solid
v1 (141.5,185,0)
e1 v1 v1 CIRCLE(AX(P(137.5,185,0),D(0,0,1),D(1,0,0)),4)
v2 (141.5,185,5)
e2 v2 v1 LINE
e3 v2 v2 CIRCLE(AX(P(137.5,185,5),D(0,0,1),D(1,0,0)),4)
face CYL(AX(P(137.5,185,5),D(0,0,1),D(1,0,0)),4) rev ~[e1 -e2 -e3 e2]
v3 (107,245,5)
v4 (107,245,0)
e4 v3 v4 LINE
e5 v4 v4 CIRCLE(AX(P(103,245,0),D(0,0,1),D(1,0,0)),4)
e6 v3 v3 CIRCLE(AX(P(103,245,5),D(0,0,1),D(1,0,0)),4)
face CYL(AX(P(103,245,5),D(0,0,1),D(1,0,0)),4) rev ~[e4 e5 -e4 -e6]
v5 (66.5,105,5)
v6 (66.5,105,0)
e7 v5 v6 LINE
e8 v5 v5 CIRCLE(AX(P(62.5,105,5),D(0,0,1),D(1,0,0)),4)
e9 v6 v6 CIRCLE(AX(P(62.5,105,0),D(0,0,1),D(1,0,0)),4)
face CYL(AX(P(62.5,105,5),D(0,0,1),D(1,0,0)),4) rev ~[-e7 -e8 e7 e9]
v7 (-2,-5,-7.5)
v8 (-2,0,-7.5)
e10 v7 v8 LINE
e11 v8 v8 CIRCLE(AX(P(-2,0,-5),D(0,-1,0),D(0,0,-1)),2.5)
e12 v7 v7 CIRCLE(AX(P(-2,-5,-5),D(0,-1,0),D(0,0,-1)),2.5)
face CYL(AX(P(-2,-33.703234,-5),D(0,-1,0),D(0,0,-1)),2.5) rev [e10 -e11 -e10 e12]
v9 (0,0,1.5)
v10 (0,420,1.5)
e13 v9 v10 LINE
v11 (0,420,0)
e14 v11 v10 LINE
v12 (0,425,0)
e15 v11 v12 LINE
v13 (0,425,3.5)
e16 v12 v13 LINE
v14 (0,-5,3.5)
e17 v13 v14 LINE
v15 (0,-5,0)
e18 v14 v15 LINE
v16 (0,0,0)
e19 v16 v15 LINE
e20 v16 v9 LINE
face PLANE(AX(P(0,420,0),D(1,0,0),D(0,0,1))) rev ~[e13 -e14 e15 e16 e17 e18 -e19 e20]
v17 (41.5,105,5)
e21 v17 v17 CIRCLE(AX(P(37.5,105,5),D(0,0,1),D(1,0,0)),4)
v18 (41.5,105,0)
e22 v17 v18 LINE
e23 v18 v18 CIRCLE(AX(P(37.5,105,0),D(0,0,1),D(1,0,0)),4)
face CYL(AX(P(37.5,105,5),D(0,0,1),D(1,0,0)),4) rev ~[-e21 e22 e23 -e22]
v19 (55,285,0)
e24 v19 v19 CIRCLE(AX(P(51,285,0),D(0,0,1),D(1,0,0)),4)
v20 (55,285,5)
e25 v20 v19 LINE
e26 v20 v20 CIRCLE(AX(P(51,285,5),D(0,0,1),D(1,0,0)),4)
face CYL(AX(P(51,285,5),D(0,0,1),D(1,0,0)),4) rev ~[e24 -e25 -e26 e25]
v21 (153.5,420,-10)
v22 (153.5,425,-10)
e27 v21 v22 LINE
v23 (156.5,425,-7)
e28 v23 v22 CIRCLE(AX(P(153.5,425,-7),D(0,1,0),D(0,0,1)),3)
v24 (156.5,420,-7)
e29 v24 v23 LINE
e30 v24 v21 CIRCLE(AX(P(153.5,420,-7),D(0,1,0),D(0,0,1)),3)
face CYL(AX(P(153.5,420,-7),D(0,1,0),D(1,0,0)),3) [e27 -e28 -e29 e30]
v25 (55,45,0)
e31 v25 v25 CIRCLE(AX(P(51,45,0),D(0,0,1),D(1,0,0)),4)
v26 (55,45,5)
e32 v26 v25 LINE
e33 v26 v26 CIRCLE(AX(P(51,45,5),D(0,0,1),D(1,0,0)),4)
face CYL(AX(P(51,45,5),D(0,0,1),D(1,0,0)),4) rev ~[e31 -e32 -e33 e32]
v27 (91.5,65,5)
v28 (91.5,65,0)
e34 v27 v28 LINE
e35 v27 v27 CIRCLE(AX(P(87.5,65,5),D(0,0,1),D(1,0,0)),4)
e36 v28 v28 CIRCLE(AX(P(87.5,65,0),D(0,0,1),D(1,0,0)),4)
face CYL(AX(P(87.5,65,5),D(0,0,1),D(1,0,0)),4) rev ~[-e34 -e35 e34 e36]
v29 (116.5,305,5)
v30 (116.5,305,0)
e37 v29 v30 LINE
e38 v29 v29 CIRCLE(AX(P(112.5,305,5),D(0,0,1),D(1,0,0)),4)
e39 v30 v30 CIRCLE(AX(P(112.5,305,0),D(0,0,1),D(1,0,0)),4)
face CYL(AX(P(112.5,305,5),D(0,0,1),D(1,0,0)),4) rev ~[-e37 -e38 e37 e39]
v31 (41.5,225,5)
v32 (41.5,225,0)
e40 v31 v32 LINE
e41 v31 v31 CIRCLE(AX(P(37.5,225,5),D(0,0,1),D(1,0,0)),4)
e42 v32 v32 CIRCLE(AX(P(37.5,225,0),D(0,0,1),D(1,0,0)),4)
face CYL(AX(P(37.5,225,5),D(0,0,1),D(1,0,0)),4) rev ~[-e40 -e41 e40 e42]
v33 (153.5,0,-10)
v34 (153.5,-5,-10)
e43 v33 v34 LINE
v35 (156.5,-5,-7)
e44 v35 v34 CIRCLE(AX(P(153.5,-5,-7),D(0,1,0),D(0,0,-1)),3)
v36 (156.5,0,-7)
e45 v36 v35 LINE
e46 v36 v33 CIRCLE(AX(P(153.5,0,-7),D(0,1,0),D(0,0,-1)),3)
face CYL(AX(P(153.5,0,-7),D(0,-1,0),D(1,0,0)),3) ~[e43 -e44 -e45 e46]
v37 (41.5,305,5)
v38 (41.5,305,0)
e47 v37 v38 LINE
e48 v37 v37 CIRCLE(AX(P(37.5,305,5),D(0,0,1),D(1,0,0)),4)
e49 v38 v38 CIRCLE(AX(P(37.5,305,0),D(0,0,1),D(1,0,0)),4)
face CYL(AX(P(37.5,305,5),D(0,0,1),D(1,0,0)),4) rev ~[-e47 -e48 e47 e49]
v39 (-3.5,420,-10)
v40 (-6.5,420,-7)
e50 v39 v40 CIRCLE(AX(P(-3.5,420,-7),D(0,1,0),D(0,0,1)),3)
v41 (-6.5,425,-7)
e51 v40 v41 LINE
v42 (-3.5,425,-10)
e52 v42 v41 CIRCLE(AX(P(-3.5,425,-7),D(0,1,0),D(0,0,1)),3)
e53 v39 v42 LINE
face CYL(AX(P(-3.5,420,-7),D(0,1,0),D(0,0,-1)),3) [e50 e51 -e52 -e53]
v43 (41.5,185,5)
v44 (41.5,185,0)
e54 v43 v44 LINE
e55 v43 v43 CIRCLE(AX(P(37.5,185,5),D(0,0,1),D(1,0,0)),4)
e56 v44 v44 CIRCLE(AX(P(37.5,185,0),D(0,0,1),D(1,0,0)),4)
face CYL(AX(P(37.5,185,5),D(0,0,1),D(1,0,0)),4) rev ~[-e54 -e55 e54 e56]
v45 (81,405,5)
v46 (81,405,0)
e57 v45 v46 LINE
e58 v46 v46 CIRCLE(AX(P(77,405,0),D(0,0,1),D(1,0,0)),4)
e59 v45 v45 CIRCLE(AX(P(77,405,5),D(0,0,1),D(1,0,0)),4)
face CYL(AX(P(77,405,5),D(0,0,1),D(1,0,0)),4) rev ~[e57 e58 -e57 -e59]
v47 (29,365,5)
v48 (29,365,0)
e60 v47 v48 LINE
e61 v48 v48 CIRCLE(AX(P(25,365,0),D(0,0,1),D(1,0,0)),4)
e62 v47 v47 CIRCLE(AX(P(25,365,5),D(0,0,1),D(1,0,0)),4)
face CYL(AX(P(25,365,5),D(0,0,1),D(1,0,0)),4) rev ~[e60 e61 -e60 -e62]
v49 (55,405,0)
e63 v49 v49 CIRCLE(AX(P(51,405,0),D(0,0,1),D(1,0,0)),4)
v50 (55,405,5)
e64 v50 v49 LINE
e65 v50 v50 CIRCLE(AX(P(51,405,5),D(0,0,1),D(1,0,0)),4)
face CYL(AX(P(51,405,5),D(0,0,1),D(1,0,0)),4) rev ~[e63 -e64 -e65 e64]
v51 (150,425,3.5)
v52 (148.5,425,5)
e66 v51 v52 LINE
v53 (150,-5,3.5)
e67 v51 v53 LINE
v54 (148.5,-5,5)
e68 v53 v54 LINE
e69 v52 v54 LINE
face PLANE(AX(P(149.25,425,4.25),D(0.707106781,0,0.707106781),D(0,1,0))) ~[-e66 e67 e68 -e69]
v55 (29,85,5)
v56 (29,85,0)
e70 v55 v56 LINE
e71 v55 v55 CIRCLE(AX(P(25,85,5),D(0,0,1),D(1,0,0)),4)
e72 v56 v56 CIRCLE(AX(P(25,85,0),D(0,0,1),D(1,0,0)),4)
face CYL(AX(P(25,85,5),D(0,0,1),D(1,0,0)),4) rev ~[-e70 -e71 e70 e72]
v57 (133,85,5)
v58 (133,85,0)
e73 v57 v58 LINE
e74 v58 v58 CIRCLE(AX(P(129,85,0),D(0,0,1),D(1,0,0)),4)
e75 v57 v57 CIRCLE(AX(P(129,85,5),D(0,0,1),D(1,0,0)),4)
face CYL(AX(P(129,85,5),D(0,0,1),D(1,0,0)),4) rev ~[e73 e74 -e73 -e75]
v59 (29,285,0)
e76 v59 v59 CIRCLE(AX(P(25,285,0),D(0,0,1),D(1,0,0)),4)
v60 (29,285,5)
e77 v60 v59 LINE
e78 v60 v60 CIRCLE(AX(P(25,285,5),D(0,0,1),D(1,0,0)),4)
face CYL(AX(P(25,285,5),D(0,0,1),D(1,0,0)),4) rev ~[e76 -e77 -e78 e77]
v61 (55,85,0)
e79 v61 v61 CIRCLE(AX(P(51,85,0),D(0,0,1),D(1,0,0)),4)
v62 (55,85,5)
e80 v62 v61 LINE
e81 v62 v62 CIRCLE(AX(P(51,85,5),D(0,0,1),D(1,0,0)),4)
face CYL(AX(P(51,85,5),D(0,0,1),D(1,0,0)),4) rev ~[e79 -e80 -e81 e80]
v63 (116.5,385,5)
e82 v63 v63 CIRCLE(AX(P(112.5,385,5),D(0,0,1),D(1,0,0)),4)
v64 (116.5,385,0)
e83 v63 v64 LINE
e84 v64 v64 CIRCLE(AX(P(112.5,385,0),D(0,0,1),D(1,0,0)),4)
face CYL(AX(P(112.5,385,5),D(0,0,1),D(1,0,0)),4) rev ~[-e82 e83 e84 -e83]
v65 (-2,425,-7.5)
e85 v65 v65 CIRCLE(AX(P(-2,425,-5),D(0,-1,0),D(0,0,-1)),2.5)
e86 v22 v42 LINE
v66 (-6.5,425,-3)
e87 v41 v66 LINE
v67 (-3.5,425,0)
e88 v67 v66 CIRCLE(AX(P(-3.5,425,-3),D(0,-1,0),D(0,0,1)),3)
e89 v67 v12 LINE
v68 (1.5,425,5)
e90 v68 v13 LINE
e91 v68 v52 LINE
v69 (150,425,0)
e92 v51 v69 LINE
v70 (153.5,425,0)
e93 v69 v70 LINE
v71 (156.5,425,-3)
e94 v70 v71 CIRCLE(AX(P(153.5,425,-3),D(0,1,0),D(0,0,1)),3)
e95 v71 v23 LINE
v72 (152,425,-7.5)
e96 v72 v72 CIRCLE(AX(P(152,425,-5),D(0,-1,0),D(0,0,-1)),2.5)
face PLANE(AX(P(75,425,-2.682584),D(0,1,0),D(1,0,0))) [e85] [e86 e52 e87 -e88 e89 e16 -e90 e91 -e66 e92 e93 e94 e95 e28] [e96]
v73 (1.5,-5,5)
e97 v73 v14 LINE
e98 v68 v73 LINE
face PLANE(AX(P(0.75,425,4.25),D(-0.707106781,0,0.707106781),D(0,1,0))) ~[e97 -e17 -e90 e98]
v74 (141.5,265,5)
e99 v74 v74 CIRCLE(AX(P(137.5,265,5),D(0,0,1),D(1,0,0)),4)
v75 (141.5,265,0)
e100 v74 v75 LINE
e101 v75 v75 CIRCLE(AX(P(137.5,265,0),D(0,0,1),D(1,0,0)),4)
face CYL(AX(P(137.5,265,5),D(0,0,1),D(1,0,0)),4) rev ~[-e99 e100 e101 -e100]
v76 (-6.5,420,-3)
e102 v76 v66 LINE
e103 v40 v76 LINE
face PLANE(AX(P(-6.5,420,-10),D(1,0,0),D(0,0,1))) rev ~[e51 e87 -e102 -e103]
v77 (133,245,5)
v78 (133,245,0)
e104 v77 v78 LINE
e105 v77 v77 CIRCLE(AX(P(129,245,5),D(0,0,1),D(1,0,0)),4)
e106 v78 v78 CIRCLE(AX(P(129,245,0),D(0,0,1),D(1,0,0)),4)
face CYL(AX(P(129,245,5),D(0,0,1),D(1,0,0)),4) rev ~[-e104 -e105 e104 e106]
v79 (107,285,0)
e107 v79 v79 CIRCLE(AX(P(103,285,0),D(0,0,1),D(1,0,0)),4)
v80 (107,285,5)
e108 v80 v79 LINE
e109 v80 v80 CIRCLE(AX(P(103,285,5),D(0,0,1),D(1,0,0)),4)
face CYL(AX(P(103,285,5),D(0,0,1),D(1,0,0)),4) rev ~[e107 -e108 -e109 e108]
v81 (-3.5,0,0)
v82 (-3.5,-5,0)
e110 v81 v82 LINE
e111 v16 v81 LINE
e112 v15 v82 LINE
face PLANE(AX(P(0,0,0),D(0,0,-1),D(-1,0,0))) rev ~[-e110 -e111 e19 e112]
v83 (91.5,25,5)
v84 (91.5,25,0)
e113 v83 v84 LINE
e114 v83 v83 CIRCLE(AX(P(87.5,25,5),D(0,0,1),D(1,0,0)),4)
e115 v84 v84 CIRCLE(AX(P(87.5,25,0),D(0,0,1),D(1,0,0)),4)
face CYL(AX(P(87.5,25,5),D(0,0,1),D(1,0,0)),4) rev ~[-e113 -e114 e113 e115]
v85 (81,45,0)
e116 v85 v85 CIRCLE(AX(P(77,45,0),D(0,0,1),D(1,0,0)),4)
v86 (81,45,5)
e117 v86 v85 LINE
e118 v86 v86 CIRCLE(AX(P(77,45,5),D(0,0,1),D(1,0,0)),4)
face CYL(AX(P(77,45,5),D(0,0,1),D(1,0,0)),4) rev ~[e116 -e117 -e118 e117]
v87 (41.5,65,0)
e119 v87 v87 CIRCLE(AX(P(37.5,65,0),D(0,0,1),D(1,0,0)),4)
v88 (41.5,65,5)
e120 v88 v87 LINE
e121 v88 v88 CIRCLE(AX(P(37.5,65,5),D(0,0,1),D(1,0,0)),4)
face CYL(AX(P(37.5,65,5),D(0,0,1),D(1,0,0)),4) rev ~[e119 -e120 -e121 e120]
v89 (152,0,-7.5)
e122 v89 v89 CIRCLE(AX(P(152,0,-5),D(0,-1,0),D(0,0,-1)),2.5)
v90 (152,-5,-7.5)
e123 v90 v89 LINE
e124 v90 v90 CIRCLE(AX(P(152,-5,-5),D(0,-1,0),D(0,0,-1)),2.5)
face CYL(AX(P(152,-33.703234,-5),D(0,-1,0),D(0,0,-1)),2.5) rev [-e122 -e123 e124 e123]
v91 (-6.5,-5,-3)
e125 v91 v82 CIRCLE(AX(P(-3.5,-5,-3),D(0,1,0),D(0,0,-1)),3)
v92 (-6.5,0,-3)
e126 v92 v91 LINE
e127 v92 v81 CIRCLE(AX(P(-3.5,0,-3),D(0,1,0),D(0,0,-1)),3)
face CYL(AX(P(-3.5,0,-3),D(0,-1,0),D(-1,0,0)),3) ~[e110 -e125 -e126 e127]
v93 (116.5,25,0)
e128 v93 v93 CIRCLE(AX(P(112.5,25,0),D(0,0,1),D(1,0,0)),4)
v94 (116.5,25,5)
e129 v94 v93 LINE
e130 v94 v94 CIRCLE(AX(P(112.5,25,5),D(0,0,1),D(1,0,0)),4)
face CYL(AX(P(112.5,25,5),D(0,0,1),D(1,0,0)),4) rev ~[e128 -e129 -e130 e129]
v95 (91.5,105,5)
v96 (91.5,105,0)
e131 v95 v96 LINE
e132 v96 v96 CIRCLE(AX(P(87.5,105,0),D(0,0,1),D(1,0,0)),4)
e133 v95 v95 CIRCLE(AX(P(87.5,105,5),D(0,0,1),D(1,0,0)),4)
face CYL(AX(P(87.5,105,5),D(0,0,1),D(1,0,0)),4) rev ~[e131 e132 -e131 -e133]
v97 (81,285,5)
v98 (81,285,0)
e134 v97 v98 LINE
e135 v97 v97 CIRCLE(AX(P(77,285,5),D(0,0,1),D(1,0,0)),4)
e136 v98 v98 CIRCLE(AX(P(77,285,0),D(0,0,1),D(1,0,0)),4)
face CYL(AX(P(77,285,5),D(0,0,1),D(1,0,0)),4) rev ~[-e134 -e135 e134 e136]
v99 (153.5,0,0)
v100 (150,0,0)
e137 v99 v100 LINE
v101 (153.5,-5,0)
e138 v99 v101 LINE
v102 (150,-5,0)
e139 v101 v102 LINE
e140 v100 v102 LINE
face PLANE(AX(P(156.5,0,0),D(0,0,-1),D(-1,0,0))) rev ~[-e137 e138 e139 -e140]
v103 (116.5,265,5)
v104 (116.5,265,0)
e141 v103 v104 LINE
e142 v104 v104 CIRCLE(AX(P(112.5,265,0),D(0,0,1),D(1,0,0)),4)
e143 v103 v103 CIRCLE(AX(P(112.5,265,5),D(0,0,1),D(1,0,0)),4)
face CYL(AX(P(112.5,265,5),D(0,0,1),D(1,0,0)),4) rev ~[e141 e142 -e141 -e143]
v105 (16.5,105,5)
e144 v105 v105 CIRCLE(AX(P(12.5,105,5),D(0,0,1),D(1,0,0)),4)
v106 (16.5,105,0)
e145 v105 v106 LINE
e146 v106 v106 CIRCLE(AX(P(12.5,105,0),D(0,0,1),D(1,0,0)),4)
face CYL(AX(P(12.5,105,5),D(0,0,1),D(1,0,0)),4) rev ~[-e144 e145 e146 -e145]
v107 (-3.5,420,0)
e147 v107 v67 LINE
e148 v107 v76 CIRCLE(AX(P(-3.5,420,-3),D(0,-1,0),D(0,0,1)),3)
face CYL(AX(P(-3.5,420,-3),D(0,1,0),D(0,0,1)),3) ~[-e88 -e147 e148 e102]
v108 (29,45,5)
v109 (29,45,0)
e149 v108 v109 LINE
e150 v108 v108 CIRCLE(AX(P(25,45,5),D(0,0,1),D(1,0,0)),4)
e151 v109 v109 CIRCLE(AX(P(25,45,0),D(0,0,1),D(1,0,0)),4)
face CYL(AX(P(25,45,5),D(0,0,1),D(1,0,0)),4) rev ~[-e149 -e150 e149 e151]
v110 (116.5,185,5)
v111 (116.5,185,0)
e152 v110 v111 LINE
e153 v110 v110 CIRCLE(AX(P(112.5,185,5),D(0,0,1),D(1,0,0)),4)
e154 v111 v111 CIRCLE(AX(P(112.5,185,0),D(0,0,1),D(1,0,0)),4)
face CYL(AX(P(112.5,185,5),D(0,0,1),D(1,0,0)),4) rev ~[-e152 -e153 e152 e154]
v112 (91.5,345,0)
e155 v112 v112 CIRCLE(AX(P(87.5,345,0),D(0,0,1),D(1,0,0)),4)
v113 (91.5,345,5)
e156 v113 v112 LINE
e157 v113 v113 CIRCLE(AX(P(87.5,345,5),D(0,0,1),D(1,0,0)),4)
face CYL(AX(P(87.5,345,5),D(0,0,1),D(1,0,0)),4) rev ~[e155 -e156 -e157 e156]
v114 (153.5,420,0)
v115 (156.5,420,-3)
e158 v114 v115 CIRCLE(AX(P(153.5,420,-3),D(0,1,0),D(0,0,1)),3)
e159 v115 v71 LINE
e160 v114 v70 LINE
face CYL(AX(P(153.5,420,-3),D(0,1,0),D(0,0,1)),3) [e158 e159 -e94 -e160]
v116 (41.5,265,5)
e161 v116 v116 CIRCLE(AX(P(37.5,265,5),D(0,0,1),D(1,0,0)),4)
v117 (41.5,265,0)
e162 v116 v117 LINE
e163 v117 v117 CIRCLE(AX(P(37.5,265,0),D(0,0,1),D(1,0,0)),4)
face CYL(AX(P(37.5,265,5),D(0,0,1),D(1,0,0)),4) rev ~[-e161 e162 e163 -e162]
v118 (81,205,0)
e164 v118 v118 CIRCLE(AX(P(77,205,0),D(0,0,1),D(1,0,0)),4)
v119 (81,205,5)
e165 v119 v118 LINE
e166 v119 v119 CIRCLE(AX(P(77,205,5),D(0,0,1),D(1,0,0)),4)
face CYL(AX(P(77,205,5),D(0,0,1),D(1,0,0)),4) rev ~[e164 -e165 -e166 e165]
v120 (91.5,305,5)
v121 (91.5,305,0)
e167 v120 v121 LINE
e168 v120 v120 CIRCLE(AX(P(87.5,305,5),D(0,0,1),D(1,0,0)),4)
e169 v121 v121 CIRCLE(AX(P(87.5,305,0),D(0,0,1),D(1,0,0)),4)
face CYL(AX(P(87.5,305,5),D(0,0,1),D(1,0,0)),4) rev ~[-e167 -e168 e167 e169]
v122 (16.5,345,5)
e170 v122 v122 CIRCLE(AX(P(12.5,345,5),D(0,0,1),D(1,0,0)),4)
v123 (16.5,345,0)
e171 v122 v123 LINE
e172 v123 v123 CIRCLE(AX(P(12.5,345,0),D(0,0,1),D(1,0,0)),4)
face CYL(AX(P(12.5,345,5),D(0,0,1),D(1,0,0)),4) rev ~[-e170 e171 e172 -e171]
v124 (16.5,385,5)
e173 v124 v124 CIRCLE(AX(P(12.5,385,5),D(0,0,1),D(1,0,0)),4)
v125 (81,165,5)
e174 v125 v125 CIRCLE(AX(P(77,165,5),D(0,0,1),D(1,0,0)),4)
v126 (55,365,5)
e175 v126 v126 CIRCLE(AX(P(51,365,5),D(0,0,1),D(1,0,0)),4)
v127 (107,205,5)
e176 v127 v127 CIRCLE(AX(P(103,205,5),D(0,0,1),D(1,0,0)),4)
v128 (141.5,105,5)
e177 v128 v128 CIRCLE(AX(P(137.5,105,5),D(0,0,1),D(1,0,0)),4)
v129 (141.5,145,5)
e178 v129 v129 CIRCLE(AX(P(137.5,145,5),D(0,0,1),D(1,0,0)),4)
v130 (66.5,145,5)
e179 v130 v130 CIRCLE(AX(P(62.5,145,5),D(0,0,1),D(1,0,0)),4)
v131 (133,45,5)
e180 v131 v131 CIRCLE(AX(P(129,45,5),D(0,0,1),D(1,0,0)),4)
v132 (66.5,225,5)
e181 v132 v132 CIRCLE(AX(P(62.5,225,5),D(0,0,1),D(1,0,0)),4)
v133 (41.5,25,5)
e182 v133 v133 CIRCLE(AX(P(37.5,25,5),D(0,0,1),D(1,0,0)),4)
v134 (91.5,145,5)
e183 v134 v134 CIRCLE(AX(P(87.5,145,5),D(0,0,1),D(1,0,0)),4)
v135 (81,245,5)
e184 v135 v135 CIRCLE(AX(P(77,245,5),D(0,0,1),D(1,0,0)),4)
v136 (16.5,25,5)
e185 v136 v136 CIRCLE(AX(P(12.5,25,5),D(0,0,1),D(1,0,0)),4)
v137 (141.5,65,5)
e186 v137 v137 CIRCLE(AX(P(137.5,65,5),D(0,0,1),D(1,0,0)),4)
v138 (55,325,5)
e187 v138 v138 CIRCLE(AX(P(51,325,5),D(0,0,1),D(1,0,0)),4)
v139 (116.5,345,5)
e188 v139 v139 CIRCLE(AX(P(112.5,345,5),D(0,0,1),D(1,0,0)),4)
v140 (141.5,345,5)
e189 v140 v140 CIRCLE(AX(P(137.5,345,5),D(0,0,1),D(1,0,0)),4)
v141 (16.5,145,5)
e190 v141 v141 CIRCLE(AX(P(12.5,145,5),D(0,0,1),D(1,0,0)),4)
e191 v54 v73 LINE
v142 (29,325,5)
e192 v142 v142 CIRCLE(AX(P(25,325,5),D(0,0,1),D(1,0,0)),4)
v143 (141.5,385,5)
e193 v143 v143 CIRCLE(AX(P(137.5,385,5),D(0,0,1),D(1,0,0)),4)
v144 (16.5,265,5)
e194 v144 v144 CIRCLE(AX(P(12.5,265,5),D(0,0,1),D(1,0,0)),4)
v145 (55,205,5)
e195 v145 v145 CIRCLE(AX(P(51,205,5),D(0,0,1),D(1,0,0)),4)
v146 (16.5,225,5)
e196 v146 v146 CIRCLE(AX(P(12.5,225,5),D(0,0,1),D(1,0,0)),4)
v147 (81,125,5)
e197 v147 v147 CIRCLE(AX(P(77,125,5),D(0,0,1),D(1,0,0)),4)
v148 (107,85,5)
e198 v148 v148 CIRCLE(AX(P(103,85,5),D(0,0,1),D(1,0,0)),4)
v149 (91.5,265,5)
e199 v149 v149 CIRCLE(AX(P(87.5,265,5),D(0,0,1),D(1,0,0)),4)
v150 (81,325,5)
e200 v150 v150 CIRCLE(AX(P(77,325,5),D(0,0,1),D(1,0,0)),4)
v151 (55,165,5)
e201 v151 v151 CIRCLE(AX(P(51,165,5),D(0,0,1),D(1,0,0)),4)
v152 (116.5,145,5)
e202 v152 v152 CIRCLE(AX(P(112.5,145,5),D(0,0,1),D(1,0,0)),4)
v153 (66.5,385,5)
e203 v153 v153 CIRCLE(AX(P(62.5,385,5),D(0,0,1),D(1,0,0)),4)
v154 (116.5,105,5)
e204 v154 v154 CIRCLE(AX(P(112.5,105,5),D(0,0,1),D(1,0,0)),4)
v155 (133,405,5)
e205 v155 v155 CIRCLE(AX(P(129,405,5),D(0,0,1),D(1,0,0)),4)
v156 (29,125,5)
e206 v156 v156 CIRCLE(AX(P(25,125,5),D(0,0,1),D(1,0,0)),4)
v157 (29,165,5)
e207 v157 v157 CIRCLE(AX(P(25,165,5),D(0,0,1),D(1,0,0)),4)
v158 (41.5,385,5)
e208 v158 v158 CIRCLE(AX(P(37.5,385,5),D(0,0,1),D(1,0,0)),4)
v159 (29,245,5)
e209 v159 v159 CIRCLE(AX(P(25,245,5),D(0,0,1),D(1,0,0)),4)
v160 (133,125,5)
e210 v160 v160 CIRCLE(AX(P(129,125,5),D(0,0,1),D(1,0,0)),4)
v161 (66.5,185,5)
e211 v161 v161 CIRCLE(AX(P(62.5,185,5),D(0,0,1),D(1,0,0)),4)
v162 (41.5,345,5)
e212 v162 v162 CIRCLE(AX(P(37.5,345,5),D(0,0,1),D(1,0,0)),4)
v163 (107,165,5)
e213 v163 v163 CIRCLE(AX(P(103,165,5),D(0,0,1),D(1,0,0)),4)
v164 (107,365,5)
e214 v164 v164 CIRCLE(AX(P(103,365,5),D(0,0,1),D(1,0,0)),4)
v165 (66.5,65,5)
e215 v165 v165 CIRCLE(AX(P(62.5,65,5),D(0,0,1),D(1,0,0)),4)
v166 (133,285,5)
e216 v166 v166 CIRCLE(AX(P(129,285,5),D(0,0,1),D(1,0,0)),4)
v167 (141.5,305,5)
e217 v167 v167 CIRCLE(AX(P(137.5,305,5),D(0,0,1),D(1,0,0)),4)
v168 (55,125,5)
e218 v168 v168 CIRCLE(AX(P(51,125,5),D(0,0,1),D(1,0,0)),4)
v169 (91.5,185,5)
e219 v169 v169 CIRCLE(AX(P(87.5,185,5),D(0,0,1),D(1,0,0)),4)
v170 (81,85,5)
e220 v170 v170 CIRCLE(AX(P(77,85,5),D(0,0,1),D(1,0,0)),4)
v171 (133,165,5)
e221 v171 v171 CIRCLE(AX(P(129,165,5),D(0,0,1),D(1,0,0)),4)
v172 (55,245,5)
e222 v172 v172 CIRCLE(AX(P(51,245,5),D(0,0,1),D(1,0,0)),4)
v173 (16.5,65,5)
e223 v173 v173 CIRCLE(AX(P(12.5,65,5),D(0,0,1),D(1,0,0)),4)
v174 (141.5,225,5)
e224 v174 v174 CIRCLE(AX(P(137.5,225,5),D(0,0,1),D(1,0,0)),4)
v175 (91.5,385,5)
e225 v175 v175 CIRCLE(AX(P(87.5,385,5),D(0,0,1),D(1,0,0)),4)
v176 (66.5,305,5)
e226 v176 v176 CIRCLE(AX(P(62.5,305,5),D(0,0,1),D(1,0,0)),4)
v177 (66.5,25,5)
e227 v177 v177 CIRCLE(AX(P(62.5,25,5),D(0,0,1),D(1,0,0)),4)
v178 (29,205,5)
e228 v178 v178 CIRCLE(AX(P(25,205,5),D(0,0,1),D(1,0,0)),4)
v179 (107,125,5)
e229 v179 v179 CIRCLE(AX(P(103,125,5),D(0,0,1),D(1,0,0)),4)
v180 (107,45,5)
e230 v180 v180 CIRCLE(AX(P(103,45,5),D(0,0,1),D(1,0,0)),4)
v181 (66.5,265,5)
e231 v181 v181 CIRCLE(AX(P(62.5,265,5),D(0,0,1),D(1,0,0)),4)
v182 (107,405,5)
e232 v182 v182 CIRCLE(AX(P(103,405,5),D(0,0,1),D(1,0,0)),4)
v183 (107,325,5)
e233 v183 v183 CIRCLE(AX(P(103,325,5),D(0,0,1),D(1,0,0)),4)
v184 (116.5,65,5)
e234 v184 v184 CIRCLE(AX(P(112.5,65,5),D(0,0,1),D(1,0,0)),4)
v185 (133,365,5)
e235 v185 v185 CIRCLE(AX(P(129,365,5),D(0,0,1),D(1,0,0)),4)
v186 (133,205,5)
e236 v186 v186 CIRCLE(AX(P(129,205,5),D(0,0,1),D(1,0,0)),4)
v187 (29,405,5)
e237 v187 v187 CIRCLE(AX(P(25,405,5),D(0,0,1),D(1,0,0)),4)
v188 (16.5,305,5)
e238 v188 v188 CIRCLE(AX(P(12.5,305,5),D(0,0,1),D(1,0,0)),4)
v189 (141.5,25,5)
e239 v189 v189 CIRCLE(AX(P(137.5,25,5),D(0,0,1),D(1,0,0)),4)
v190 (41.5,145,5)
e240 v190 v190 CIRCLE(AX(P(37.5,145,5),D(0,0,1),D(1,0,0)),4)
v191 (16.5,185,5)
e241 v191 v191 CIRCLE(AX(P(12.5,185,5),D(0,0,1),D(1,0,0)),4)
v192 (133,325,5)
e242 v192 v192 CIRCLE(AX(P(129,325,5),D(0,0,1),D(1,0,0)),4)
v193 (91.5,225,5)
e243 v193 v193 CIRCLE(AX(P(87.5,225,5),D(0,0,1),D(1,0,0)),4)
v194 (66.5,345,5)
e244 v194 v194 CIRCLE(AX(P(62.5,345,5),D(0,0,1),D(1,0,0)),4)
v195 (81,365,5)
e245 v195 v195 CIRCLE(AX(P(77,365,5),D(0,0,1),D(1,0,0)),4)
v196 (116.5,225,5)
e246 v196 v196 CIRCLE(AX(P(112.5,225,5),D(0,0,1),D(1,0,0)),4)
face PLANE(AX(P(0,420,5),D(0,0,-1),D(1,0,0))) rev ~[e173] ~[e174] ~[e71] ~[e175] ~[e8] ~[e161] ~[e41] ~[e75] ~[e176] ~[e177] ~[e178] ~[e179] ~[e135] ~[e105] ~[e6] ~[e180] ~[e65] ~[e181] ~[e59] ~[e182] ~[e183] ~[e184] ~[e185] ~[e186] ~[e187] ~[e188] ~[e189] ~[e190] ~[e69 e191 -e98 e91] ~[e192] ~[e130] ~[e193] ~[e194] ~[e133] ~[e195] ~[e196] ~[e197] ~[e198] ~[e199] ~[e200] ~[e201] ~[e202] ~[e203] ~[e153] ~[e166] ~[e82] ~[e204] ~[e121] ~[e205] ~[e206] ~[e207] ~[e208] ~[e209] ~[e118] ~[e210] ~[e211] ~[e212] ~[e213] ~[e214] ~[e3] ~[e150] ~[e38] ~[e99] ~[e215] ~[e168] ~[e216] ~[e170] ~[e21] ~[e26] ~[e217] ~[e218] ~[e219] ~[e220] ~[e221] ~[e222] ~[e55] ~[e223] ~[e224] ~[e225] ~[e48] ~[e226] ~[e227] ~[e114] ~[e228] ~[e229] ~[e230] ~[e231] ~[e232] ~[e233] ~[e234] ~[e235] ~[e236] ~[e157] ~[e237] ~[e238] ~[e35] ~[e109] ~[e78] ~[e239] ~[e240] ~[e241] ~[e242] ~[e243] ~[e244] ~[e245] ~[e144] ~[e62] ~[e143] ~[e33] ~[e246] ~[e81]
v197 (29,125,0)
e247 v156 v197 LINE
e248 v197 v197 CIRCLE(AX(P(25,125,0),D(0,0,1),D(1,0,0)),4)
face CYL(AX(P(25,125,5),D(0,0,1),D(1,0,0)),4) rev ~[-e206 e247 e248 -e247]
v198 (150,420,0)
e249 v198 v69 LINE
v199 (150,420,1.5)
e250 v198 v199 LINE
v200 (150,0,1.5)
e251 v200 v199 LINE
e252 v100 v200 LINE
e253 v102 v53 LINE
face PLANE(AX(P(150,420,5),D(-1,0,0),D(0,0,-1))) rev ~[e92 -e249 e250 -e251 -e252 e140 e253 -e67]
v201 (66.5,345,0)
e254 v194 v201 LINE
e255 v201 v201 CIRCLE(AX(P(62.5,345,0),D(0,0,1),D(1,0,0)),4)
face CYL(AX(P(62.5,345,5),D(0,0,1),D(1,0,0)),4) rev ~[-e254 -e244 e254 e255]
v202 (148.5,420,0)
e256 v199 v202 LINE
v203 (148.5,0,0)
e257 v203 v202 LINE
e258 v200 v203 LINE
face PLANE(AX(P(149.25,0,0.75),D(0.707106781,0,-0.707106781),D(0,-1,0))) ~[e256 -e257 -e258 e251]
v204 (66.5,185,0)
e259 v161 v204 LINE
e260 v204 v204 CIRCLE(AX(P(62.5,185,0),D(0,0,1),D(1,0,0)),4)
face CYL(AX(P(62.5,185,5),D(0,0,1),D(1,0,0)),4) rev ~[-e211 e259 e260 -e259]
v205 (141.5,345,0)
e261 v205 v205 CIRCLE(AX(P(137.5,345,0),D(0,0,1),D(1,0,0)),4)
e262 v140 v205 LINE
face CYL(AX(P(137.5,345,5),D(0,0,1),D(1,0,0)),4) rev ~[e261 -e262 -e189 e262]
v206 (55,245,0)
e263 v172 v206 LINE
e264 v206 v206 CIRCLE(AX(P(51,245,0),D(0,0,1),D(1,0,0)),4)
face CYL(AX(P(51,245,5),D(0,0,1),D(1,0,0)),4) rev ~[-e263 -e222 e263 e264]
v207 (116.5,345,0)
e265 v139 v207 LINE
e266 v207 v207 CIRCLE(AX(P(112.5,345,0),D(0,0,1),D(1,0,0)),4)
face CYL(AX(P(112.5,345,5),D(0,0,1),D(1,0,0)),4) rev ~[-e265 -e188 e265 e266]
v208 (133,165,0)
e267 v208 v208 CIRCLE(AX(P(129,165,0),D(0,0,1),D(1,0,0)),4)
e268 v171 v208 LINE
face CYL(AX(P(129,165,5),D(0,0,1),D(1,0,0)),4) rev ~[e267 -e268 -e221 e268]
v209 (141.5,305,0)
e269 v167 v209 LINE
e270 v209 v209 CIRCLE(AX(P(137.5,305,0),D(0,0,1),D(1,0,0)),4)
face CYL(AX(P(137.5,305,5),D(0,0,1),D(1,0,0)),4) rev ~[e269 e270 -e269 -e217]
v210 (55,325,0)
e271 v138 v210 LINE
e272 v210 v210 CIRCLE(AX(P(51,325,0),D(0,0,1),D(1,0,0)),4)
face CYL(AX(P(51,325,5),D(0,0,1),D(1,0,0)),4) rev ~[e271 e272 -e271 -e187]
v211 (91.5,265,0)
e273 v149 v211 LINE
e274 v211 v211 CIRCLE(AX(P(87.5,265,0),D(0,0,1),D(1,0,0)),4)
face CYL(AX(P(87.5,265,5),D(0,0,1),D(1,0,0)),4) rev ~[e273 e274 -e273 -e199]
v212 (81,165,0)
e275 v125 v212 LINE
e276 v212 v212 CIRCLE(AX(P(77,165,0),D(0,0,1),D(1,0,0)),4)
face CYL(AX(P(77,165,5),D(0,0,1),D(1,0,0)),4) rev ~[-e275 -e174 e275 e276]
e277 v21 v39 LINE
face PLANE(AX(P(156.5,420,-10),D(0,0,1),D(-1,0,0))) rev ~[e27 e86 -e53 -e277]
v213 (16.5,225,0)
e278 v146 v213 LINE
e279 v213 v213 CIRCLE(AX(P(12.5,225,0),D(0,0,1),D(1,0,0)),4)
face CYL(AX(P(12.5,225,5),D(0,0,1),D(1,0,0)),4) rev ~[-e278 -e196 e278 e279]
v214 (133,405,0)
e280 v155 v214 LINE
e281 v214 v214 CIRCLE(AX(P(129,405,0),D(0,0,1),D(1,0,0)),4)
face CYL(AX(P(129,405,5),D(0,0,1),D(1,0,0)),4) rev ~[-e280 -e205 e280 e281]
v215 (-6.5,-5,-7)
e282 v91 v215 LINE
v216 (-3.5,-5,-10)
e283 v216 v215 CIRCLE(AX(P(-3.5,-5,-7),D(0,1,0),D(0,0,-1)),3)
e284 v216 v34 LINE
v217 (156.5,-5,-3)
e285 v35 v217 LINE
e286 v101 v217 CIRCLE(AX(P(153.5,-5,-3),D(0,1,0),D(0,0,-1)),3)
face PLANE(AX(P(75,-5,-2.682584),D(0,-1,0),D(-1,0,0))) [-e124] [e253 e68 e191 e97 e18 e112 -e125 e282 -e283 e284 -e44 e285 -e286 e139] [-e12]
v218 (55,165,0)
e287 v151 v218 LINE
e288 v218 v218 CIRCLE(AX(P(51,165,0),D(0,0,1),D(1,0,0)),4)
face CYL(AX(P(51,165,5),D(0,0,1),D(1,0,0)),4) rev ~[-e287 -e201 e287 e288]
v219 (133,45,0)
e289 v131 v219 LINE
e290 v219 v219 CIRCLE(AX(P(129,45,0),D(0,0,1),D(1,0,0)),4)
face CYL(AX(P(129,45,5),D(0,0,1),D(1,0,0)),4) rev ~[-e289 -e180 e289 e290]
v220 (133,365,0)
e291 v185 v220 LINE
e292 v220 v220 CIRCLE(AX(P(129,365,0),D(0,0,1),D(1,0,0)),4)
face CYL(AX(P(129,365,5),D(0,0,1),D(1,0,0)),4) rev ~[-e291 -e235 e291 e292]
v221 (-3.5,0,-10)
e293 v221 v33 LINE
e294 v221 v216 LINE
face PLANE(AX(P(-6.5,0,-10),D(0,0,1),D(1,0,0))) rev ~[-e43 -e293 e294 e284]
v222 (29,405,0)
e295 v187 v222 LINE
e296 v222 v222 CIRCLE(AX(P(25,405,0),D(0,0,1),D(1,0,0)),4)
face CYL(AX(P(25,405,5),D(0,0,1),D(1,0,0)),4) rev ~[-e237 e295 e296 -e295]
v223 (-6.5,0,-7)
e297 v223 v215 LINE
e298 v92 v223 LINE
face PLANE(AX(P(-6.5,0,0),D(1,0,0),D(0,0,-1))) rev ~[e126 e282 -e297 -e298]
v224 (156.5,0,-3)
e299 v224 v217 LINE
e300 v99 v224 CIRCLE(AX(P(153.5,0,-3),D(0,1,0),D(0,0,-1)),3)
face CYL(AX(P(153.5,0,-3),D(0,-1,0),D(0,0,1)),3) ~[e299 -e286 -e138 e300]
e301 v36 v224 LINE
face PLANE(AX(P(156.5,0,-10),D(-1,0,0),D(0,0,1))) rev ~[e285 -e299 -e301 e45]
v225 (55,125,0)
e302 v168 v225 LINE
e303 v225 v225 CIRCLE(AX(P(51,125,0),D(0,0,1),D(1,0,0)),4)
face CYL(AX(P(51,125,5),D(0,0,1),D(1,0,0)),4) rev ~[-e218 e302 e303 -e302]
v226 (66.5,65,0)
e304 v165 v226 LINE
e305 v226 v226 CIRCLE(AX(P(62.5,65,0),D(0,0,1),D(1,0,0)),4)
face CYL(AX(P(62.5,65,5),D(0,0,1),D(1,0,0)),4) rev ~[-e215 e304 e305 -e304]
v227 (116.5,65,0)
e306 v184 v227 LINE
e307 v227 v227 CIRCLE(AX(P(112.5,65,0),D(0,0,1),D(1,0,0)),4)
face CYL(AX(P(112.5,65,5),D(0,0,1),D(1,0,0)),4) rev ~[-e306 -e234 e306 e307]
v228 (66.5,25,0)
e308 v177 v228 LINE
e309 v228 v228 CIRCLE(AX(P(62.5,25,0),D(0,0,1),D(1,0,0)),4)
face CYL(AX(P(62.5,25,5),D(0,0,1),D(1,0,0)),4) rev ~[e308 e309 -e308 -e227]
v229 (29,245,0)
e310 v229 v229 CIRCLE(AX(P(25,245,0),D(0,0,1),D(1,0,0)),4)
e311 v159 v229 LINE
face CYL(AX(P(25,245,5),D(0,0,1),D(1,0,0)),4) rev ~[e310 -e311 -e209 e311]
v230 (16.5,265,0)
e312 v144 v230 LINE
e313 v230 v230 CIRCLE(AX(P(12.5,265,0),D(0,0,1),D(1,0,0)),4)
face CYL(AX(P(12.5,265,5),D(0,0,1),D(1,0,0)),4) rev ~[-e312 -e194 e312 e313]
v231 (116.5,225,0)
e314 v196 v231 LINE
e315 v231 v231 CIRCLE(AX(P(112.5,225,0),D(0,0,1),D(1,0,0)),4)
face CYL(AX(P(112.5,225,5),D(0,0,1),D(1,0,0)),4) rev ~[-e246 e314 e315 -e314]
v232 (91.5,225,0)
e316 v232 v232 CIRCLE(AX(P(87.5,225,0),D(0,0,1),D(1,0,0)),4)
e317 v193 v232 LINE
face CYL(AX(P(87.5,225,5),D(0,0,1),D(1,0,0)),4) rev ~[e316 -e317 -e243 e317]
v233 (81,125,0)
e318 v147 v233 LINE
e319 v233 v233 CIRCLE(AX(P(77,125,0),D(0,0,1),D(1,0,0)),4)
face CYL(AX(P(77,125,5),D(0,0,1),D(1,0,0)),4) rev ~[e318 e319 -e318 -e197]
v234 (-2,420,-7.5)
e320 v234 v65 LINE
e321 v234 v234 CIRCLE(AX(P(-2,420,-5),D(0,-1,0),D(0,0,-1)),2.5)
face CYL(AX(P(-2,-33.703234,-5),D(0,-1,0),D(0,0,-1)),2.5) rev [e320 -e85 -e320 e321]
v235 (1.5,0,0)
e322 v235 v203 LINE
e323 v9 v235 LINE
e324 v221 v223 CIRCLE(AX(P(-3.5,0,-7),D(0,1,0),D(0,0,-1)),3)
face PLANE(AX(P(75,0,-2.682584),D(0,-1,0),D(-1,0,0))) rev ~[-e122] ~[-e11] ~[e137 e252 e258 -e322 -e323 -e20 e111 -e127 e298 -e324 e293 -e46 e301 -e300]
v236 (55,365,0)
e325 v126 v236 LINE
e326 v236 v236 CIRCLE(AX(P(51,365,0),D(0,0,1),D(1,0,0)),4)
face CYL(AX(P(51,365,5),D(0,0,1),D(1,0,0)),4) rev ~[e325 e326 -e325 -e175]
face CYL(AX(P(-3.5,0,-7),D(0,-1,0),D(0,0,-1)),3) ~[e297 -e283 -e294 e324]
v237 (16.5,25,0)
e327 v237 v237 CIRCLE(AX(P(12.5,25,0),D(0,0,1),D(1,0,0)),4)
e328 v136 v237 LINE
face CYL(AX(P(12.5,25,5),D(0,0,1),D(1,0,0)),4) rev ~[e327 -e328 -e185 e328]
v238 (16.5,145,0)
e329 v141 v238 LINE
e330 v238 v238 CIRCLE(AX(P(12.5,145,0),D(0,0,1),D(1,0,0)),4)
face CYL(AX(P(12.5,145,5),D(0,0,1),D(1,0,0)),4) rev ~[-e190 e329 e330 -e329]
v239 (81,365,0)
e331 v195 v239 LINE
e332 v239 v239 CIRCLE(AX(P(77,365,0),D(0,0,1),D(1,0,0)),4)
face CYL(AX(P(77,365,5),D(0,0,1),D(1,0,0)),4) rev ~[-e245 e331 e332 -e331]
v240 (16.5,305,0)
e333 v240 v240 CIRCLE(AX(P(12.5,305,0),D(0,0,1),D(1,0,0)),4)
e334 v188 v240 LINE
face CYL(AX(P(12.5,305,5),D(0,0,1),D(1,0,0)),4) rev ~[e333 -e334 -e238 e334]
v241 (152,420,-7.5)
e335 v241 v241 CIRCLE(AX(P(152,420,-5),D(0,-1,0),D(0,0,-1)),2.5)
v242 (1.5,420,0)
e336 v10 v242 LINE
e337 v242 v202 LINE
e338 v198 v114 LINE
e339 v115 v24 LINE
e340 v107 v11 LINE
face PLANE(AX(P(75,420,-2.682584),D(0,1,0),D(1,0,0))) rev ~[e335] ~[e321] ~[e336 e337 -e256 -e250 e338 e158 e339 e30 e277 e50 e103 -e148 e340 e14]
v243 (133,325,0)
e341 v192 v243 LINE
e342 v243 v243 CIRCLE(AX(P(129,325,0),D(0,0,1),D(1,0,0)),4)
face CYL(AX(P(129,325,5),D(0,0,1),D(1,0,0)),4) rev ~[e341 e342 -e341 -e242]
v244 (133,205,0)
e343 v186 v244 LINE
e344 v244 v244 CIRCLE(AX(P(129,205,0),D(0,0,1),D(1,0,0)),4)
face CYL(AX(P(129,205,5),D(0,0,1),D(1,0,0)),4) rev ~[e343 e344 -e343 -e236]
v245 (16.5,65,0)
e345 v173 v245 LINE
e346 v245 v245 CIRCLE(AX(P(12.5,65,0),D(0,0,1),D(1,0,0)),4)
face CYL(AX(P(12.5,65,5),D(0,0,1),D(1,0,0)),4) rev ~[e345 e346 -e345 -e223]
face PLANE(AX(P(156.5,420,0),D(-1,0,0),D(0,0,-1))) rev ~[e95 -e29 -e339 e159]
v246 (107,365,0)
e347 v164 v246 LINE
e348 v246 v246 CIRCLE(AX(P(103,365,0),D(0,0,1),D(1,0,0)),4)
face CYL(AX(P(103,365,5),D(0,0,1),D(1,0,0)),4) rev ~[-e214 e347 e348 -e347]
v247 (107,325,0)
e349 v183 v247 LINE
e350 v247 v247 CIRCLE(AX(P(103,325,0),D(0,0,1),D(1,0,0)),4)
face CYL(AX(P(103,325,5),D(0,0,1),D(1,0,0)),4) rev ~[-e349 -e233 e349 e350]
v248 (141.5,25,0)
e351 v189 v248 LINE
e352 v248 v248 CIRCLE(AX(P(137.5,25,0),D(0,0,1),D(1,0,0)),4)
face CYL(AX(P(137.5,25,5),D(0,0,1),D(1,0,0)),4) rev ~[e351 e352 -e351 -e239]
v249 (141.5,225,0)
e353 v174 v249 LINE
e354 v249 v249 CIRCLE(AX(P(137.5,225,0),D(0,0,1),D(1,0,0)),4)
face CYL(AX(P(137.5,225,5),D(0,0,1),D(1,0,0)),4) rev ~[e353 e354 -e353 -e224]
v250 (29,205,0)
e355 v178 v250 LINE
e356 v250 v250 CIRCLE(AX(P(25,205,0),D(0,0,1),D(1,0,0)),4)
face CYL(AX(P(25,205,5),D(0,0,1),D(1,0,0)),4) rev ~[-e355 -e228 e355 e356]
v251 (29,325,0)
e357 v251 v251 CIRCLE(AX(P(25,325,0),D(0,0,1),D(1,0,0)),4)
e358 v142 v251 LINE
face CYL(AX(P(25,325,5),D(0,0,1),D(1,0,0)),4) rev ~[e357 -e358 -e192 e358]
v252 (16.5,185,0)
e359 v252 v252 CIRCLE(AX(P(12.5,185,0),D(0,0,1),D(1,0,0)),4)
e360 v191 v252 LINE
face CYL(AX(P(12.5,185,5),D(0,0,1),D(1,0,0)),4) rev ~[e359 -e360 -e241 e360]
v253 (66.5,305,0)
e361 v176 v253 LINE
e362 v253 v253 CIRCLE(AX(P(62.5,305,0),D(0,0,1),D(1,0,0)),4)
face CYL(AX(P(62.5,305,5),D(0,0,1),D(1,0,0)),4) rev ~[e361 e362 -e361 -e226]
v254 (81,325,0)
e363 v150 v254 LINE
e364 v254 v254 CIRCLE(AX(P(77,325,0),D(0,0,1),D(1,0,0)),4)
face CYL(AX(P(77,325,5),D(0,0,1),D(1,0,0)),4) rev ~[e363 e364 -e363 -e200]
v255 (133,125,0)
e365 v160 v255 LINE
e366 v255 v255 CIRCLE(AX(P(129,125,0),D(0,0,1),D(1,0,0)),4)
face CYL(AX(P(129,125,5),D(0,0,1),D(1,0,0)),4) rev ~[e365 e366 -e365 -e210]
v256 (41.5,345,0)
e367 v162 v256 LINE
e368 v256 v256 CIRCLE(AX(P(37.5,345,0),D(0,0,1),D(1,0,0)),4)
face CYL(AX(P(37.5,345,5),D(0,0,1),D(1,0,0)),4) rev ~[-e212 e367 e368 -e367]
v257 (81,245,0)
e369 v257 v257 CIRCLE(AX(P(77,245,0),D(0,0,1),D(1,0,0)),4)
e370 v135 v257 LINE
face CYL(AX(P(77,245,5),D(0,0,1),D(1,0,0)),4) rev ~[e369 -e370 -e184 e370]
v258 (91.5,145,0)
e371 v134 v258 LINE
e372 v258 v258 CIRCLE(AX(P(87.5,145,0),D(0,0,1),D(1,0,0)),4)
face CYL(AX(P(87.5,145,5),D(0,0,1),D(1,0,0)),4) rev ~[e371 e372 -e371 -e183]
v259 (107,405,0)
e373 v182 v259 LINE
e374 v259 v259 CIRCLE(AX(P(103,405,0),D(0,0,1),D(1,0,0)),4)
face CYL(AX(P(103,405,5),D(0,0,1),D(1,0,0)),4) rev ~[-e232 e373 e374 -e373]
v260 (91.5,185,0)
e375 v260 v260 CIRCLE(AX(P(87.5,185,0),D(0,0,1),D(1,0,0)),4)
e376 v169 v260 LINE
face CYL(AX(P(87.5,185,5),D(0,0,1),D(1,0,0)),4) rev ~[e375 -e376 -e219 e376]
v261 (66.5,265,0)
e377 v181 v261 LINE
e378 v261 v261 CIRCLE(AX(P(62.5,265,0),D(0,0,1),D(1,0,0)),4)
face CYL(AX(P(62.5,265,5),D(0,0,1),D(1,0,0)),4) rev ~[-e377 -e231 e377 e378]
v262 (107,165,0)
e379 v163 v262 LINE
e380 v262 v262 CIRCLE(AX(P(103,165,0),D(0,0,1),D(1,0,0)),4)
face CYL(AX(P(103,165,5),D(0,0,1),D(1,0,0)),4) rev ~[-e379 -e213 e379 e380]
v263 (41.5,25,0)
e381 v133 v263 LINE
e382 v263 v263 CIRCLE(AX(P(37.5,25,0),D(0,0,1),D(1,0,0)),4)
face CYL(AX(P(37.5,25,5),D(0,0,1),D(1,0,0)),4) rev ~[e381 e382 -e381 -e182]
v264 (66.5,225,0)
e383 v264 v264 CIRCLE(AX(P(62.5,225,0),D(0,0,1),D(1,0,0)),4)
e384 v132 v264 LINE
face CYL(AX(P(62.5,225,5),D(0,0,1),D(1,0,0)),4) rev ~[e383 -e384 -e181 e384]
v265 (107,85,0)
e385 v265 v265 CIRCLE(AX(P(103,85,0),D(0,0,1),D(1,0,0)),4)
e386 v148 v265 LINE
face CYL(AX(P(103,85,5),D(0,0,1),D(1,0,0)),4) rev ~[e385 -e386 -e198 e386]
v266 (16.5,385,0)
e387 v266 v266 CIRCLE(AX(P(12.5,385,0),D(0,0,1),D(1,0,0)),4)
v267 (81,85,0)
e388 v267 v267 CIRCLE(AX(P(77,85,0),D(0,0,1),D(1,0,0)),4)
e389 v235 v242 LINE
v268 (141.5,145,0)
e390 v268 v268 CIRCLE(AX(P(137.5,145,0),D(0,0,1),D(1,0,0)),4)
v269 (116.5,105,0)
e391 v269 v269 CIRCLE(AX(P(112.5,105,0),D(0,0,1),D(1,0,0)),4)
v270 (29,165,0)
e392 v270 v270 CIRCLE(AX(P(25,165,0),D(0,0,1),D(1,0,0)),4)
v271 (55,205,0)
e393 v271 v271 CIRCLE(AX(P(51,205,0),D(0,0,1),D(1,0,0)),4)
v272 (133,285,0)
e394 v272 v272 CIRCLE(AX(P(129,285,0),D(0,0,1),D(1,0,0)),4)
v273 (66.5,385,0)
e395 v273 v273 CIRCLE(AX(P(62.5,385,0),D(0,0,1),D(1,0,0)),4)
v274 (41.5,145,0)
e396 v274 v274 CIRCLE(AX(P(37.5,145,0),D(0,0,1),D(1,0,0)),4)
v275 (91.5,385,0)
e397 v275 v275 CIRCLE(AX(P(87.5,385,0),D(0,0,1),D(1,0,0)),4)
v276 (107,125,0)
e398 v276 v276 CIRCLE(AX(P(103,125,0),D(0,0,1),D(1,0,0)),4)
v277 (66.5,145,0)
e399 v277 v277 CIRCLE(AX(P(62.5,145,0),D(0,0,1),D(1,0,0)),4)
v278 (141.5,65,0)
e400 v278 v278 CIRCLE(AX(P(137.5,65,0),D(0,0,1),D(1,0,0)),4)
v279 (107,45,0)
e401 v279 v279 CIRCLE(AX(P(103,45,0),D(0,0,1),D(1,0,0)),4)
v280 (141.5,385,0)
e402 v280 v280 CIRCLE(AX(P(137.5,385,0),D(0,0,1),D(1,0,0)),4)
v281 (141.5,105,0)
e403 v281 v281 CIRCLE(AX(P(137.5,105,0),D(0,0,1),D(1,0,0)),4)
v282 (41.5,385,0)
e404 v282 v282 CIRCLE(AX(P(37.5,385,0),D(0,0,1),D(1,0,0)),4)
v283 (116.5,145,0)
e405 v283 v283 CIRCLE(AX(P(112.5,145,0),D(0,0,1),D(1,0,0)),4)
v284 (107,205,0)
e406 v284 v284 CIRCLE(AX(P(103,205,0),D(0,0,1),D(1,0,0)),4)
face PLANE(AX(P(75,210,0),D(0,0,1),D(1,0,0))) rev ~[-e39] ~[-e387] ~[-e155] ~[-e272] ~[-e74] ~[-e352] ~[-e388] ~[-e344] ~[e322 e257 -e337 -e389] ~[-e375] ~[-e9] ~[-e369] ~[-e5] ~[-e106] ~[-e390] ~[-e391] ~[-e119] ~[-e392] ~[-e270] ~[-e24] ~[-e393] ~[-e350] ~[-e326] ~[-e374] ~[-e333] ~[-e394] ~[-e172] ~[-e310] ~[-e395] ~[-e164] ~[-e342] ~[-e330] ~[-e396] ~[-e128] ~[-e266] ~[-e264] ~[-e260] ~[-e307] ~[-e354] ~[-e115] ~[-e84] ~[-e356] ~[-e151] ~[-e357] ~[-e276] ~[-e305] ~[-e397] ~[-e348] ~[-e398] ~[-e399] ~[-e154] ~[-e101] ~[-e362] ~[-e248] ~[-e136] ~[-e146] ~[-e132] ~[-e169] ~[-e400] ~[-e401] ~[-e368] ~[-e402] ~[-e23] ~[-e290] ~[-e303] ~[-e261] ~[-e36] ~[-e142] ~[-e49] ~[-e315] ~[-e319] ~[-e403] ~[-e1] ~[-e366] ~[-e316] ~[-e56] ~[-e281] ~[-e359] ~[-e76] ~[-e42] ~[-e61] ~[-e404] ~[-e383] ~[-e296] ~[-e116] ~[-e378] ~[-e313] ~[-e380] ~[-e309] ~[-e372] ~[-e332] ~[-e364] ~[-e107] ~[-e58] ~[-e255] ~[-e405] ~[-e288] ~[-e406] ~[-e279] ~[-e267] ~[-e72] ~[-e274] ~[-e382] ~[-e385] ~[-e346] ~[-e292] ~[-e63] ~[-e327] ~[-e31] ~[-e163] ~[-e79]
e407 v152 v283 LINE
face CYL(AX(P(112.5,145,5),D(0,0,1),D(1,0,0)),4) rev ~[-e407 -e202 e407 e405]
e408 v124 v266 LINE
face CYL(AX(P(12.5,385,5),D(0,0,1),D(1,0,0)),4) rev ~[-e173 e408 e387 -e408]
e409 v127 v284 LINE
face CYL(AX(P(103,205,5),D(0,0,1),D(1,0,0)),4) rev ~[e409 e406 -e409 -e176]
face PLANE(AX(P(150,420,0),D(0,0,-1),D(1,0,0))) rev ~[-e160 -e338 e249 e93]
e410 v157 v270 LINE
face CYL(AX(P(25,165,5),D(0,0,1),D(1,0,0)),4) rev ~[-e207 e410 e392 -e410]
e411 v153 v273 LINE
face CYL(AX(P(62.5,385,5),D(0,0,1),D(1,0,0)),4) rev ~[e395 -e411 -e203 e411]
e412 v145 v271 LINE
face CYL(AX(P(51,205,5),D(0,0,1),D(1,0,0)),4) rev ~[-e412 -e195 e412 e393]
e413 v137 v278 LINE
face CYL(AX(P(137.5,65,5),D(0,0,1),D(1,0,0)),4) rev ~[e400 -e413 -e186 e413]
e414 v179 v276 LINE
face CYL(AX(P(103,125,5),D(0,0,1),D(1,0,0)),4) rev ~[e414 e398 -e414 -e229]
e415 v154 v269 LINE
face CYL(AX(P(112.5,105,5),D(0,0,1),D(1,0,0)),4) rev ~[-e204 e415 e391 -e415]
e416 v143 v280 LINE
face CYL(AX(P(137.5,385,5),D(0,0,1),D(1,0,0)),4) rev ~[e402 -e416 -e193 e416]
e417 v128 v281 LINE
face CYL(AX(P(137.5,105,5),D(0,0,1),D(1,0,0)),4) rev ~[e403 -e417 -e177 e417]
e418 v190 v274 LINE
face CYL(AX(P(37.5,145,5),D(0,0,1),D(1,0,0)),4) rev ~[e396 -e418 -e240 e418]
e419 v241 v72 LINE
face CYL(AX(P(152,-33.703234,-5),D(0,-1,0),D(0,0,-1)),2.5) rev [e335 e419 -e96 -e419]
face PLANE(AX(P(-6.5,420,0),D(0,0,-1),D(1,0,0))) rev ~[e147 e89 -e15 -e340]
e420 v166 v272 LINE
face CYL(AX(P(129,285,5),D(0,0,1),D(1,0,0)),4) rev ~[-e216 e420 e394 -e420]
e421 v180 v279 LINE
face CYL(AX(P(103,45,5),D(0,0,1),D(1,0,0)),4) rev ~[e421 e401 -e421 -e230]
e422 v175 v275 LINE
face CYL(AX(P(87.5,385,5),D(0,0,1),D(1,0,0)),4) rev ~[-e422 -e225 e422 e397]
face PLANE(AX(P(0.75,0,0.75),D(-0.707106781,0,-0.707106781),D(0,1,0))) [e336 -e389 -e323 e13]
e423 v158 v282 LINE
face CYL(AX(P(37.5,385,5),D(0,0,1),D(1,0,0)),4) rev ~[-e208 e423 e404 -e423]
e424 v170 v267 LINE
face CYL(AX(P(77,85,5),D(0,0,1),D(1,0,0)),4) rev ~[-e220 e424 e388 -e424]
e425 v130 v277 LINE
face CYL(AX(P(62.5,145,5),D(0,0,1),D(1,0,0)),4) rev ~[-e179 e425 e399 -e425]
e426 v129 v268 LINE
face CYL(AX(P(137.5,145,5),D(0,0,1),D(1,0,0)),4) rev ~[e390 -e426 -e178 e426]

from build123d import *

# Parameters (mm, degrees)
SKETCH1_W               = 150
SKETCH1_H               = 420
BOSS_EXTRUDE1_DEPTH     = 5
CUT_EXTRUDE1_REACH      = 448.01
SKETCH2_R               = 4
LPATTERN1_COUNT         = 10
LPATTERN1_PITCH         = 40
BOSS_EXTRUDE2_DEPTH     = 5
BOSS_EXTRUDE3_DEPTH     = 5
CUT_EXTRUDE2_DEPTH      = 458.703233548
CUT_EXTRUDE2_DEPTH_BACK = 458.703233548
SKETCH6_R               = 2.5
SKETCH6_W               = 6.5
SKETCH6_H               = 5
FILLET1_R               = 3
CHAMFER1_SIZE           = 1.5


with BuildPart() as part:
    # Sketch1 → Boss-Extrude1 (new body)
    with BuildSketch(Plane.XY):
        with Locations((75, 210)):
            Rectangle(SKETCH1_W, SKETCH1_H)
    extrude(amount=BOSS_EXTRUDE1_DEPTH)

    # Sketch2 → Cut-Extrude1 (cut, up to next)
    with BuildSketch(Plane.XY.offset(5), mode=Mode.PRIVATE) as cut_extrude1_sk1:
        with Locations((25, 405)):
            Circle(SKETCH2_R)
    cut_extrude1_tool1 = extrude(cut_extrude1_sk1.sketch, amount=-CUT_EXTRUDE1_REACH, mode=Mode.PRIVATE) & part.part
    # Sketch2 → Cut-Extrude1 (cut, up to next)
    with BuildSketch(Plane.XY.offset(5), mode=Mode.PRIVATE) as cut_extrude1_sk2:
        with Locations((51, 405)):
            Circle(SKETCH2_R)
    cut_extrude1_tool2 = extrude(cut_extrude1_sk2.sketch, amount=-CUT_EXTRUDE1_REACH, mode=Mode.PRIVATE) & part.part
    # Sketch2 → Cut-Extrude1 (cut, up to next)
    with BuildSketch(Plane.XY.offset(5), mode=Mode.PRIVATE) as cut_extrude1_sk3:
        with Locations((77, 405)):
            Circle(SKETCH2_R)
    cut_extrude1_tool3 = extrude(cut_extrude1_sk3.sketch, amount=-CUT_EXTRUDE1_REACH, mode=Mode.PRIVATE) & part.part
    # Sketch2 → Cut-Extrude1 (cut, up to next)
    with BuildSketch(Plane.XY.offset(5), mode=Mode.PRIVATE) as cut_extrude1_sk4:
        with Locations((103, 405)):
            Circle(SKETCH2_R)
    cut_extrude1_tool4 = extrude(cut_extrude1_sk4.sketch, amount=-CUT_EXTRUDE1_REACH, mode=Mode.PRIVATE) & part.part
    # Sketch2 → Cut-Extrude1 (cut, up to next)
    with BuildSketch(Plane.XY.offset(5), mode=Mode.PRIVATE) as cut_extrude1_sk5:
        with Locations((129, 405)):
            Circle(SKETCH2_R)
    cut_extrude1_tool5 = extrude(cut_extrude1_sk5.sketch, amount=-CUT_EXTRUDE1_REACH, mode=Mode.PRIVATE) & part.part
    # Sketch2 → Cut-Extrude1 (cut, up to next)
    with BuildSketch(Plane.XY.offset(5), mode=Mode.PRIVATE) as cut_extrude1_sk6:
        with Locations((12.5, 385)):
            Circle(SKETCH2_R)
    cut_extrude1_tool6 = extrude(cut_extrude1_sk6.sketch, amount=-CUT_EXTRUDE1_REACH, mode=Mode.PRIVATE) & part.part
    # Sketch2 → Cut-Extrude1 (cut, up to next)
    with BuildSketch(Plane.XY.offset(5), mode=Mode.PRIVATE) as cut_extrude1_sk7:
        with Locations((37.5, 385)):
            Circle(SKETCH2_R)
    cut_extrude1_tool7 = extrude(cut_extrude1_sk7.sketch, amount=-CUT_EXTRUDE1_REACH, mode=Mode.PRIVATE) & part.part
    # Sketch2 → Cut-Extrude1 (cut, up to next)
    with BuildSketch(Plane.XY.offset(5), mode=Mode.PRIVATE) as cut_extrude1_sk8:
        with Locations((62.5, 385)):
            Circle(SKETCH2_R)
    cut_extrude1_tool8 = extrude(cut_extrude1_sk8.sketch, amount=-CUT_EXTRUDE1_REACH, mode=Mode.PRIVATE) & part.part
    # Sketch2 → Cut-Extrude1 (cut, up to next)
    with BuildSketch(Plane.XY.offset(5), mode=Mode.PRIVATE) as cut_extrude1_sk9:
        with Locations((87.5, 385)):
            Circle(SKETCH2_R)
    cut_extrude1_tool9 = extrude(cut_extrude1_sk9.sketch, amount=-CUT_EXTRUDE1_REACH, mode=Mode.PRIVATE) & part.part
    # Sketch2 → Cut-Extrude1 (cut, up to next)
    with BuildSketch(Plane.XY.offset(5), mode=Mode.PRIVATE) as cut_extrude1_sk10:
        with Locations((112.5, 385)):
            Circle(SKETCH2_R)
    cut_extrude1_tool10 = extrude(cut_extrude1_sk10.sketch, amount=-CUT_EXTRUDE1_REACH, mode=Mode.PRIVATE) & part.part
    # Sketch2 → Cut-Extrude1 (cut, up to next)
    with BuildSketch(Plane.XY.offset(5), mode=Mode.PRIVATE) as cut_extrude1_sk11:
        with Locations((137.5, 385)):
            Circle(SKETCH2_R)
    cut_extrude1_tool11 = extrude(cut_extrude1_sk11.sketch, amount=-CUT_EXTRUDE1_REACH, mode=Mode.PRIVATE) & part.part
    cut_extrude1_1 = cut_extrude1_tool1.solids().sort_by_distance((25, 405, 5))[0]
    add(cut_extrude1_1, mode=Mode.SUBTRACT)
    cut_extrude1_2 = cut_extrude1_tool2.solids().sort_by_distance((51, 405, 5))[0]
    add(cut_extrude1_2, mode=Mode.SUBTRACT)
    cut_extrude1_3 = cut_extrude1_tool3.solids().sort_by_distance((77, 405, 5))[0]
    add(cut_extrude1_3, mode=Mode.SUBTRACT)
    cut_extrude1_4 = cut_extrude1_tool4.solids().sort_by_distance((103, 405, 5))[0]
    add(cut_extrude1_4, mode=Mode.SUBTRACT)
    cut_extrude1_5 = cut_extrude1_tool5.solids().sort_by_distance((129, 405, 5))[0]
    add(cut_extrude1_5, mode=Mode.SUBTRACT)
    cut_extrude1_6 = cut_extrude1_tool6.solids().sort_by_distance((12.5, 385, 5))[0]
    add(cut_extrude1_6, mode=Mode.SUBTRACT)
    cut_extrude1_7 = cut_extrude1_tool7.solids().sort_by_distance((37.5, 385, 5))[0]
    add(cut_extrude1_7, mode=Mode.SUBTRACT)
    cut_extrude1_8 = cut_extrude1_tool8.solids().sort_by_distance((62.5, 385, 5))[0]
    add(cut_extrude1_8, mode=Mode.SUBTRACT)
    cut_extrude1_9 = cut_extrude1_tool9.solids().sort_by_distance((87.5, 385, 5))[0]
    add(cut_extrude1_9, mode=Mode.SUBTRACT)
    cut_extrude1_10 = cut_extrude1_tool10.solids().sort_by_distance((112.5, 385, 5))[0]
    add(cut_extrude1_10, mode=Mode.SUBTRACT)
    cut_extrude1_11 = cut_extrude1_tool11.solids().sort_by_distance((137.5, 385, 5))[0]
    add(cut_extrude1_11, mode=Mode.SUBTRACT)
    cut_extrude1 = cut_extrude1_1 + cut_extrude1_2 + cut_extrude1_3 + cut_extrude1_4 + cut_extrude1_5 + cut_extrude1_6 + cut_extrude1_7 + cut_extrude1_8 + cut_extrude1_9 + cut_extrude1_10 + cut_extrude1_11  # Cut-Extrude1 as one shape, for the pattern or mirror that repeats it

    # LPattern1: Cut-Extrude1 ×10
    with Locations(*[(0, -i * LPATTERN1_PITCH, 0) for i in range(1, LPATTERN1_COUNT)]):
        add(cut_extrude1, mode=Mode.SUBTRACT)

    # Sketch3 → Boss-Extrude2 (add)
    with BuildSketch(Plane(origin=(0, 0, 0), x_dir=(-1, 0, 0), z_dir=(0, -1, 0))):
        Polygon((6.5, 10), (-156.5, 10), (-156.5, 0), (-150, 0), (-150, -5), (0, -5), (0, 0), (6.5, 0), align=None)
    extrude(amount=BOSS_EXTRUDE2_DEPTH)

    # Sketch4 → Boss-Extrude3 (add)
    with BuildSketch(Plane(origin=(0, 420, 0), x_dir=(1, 0, 0), z_dir=(0, 1, 0))):
        Polygon((150, -5), (150, 0), (156.5, 0), (156.5, 10), (-6.5, 10), (-6.5, 0), (0, 0), (0, -5), align=None)
    extrude(amount=BOSS_EXTRUDE3_DEPTH)

    # Sketch6 → Cut-Extrude2 (cut, two sides: drawn at the far end of the back side and taken through both)
    with BuildSketch(Plane(origin=(0, 425, 0), x_dir=(1, 0, 0), z_dir=(0, 1, 0)).offset(-CUT_EXTRUDE2_DEPTH_BACK)):
        with Locations(Location((-2, 5, 0), (0, 0, 90))):
            Circle(SKETCH6_R)
        with Locations(Location((152, 5, 0), (0, 0, 90))):
            Circle(SKETCH6_R)
        with Locations((153.25, -2.5)):
            Rectangle(SKETCH6_W, SKETCH6_H)
        with Locations((-3.25, -2.5)):
            Rectangle(SKETCH6_W, SKETCH6_H)
    extrude(amount=CUT_EXTRUDE2_DEPTH + CUT_EXTRUDE2_DEPTH_BACK, mode=Mode.SUBTRACT)

    # Fillet1
    fillet1_edges = [part.edges().sort_by_distance(p)[0] for p in [
        (-6.5, -2.5, 0),
        (-6.5, -2.5, -10),
        (156.5, -2.5, -10),
        (156.5, -2.5, 0),
        (-6.5, 422.5, -10),
        (-6.5, 422.5, 0),
        (156.5, 422.5, 0),
        (156.5, 422.5, -10),
    ]]
    fillet(fillet1_edges, radius=FILLET1_R)

    # Chamfer1
    chamfer1_edges = [part.edges().sort_by_distance(p)[0] for p in [
        (150, 210, 5),
        (0, 210, 5),
        (150, 210, 0),
        (0, 210, 0),
    ]]
    chamfer(chamfer1_edges, length=CHAMFER1_SIZE)


solid = part.part
